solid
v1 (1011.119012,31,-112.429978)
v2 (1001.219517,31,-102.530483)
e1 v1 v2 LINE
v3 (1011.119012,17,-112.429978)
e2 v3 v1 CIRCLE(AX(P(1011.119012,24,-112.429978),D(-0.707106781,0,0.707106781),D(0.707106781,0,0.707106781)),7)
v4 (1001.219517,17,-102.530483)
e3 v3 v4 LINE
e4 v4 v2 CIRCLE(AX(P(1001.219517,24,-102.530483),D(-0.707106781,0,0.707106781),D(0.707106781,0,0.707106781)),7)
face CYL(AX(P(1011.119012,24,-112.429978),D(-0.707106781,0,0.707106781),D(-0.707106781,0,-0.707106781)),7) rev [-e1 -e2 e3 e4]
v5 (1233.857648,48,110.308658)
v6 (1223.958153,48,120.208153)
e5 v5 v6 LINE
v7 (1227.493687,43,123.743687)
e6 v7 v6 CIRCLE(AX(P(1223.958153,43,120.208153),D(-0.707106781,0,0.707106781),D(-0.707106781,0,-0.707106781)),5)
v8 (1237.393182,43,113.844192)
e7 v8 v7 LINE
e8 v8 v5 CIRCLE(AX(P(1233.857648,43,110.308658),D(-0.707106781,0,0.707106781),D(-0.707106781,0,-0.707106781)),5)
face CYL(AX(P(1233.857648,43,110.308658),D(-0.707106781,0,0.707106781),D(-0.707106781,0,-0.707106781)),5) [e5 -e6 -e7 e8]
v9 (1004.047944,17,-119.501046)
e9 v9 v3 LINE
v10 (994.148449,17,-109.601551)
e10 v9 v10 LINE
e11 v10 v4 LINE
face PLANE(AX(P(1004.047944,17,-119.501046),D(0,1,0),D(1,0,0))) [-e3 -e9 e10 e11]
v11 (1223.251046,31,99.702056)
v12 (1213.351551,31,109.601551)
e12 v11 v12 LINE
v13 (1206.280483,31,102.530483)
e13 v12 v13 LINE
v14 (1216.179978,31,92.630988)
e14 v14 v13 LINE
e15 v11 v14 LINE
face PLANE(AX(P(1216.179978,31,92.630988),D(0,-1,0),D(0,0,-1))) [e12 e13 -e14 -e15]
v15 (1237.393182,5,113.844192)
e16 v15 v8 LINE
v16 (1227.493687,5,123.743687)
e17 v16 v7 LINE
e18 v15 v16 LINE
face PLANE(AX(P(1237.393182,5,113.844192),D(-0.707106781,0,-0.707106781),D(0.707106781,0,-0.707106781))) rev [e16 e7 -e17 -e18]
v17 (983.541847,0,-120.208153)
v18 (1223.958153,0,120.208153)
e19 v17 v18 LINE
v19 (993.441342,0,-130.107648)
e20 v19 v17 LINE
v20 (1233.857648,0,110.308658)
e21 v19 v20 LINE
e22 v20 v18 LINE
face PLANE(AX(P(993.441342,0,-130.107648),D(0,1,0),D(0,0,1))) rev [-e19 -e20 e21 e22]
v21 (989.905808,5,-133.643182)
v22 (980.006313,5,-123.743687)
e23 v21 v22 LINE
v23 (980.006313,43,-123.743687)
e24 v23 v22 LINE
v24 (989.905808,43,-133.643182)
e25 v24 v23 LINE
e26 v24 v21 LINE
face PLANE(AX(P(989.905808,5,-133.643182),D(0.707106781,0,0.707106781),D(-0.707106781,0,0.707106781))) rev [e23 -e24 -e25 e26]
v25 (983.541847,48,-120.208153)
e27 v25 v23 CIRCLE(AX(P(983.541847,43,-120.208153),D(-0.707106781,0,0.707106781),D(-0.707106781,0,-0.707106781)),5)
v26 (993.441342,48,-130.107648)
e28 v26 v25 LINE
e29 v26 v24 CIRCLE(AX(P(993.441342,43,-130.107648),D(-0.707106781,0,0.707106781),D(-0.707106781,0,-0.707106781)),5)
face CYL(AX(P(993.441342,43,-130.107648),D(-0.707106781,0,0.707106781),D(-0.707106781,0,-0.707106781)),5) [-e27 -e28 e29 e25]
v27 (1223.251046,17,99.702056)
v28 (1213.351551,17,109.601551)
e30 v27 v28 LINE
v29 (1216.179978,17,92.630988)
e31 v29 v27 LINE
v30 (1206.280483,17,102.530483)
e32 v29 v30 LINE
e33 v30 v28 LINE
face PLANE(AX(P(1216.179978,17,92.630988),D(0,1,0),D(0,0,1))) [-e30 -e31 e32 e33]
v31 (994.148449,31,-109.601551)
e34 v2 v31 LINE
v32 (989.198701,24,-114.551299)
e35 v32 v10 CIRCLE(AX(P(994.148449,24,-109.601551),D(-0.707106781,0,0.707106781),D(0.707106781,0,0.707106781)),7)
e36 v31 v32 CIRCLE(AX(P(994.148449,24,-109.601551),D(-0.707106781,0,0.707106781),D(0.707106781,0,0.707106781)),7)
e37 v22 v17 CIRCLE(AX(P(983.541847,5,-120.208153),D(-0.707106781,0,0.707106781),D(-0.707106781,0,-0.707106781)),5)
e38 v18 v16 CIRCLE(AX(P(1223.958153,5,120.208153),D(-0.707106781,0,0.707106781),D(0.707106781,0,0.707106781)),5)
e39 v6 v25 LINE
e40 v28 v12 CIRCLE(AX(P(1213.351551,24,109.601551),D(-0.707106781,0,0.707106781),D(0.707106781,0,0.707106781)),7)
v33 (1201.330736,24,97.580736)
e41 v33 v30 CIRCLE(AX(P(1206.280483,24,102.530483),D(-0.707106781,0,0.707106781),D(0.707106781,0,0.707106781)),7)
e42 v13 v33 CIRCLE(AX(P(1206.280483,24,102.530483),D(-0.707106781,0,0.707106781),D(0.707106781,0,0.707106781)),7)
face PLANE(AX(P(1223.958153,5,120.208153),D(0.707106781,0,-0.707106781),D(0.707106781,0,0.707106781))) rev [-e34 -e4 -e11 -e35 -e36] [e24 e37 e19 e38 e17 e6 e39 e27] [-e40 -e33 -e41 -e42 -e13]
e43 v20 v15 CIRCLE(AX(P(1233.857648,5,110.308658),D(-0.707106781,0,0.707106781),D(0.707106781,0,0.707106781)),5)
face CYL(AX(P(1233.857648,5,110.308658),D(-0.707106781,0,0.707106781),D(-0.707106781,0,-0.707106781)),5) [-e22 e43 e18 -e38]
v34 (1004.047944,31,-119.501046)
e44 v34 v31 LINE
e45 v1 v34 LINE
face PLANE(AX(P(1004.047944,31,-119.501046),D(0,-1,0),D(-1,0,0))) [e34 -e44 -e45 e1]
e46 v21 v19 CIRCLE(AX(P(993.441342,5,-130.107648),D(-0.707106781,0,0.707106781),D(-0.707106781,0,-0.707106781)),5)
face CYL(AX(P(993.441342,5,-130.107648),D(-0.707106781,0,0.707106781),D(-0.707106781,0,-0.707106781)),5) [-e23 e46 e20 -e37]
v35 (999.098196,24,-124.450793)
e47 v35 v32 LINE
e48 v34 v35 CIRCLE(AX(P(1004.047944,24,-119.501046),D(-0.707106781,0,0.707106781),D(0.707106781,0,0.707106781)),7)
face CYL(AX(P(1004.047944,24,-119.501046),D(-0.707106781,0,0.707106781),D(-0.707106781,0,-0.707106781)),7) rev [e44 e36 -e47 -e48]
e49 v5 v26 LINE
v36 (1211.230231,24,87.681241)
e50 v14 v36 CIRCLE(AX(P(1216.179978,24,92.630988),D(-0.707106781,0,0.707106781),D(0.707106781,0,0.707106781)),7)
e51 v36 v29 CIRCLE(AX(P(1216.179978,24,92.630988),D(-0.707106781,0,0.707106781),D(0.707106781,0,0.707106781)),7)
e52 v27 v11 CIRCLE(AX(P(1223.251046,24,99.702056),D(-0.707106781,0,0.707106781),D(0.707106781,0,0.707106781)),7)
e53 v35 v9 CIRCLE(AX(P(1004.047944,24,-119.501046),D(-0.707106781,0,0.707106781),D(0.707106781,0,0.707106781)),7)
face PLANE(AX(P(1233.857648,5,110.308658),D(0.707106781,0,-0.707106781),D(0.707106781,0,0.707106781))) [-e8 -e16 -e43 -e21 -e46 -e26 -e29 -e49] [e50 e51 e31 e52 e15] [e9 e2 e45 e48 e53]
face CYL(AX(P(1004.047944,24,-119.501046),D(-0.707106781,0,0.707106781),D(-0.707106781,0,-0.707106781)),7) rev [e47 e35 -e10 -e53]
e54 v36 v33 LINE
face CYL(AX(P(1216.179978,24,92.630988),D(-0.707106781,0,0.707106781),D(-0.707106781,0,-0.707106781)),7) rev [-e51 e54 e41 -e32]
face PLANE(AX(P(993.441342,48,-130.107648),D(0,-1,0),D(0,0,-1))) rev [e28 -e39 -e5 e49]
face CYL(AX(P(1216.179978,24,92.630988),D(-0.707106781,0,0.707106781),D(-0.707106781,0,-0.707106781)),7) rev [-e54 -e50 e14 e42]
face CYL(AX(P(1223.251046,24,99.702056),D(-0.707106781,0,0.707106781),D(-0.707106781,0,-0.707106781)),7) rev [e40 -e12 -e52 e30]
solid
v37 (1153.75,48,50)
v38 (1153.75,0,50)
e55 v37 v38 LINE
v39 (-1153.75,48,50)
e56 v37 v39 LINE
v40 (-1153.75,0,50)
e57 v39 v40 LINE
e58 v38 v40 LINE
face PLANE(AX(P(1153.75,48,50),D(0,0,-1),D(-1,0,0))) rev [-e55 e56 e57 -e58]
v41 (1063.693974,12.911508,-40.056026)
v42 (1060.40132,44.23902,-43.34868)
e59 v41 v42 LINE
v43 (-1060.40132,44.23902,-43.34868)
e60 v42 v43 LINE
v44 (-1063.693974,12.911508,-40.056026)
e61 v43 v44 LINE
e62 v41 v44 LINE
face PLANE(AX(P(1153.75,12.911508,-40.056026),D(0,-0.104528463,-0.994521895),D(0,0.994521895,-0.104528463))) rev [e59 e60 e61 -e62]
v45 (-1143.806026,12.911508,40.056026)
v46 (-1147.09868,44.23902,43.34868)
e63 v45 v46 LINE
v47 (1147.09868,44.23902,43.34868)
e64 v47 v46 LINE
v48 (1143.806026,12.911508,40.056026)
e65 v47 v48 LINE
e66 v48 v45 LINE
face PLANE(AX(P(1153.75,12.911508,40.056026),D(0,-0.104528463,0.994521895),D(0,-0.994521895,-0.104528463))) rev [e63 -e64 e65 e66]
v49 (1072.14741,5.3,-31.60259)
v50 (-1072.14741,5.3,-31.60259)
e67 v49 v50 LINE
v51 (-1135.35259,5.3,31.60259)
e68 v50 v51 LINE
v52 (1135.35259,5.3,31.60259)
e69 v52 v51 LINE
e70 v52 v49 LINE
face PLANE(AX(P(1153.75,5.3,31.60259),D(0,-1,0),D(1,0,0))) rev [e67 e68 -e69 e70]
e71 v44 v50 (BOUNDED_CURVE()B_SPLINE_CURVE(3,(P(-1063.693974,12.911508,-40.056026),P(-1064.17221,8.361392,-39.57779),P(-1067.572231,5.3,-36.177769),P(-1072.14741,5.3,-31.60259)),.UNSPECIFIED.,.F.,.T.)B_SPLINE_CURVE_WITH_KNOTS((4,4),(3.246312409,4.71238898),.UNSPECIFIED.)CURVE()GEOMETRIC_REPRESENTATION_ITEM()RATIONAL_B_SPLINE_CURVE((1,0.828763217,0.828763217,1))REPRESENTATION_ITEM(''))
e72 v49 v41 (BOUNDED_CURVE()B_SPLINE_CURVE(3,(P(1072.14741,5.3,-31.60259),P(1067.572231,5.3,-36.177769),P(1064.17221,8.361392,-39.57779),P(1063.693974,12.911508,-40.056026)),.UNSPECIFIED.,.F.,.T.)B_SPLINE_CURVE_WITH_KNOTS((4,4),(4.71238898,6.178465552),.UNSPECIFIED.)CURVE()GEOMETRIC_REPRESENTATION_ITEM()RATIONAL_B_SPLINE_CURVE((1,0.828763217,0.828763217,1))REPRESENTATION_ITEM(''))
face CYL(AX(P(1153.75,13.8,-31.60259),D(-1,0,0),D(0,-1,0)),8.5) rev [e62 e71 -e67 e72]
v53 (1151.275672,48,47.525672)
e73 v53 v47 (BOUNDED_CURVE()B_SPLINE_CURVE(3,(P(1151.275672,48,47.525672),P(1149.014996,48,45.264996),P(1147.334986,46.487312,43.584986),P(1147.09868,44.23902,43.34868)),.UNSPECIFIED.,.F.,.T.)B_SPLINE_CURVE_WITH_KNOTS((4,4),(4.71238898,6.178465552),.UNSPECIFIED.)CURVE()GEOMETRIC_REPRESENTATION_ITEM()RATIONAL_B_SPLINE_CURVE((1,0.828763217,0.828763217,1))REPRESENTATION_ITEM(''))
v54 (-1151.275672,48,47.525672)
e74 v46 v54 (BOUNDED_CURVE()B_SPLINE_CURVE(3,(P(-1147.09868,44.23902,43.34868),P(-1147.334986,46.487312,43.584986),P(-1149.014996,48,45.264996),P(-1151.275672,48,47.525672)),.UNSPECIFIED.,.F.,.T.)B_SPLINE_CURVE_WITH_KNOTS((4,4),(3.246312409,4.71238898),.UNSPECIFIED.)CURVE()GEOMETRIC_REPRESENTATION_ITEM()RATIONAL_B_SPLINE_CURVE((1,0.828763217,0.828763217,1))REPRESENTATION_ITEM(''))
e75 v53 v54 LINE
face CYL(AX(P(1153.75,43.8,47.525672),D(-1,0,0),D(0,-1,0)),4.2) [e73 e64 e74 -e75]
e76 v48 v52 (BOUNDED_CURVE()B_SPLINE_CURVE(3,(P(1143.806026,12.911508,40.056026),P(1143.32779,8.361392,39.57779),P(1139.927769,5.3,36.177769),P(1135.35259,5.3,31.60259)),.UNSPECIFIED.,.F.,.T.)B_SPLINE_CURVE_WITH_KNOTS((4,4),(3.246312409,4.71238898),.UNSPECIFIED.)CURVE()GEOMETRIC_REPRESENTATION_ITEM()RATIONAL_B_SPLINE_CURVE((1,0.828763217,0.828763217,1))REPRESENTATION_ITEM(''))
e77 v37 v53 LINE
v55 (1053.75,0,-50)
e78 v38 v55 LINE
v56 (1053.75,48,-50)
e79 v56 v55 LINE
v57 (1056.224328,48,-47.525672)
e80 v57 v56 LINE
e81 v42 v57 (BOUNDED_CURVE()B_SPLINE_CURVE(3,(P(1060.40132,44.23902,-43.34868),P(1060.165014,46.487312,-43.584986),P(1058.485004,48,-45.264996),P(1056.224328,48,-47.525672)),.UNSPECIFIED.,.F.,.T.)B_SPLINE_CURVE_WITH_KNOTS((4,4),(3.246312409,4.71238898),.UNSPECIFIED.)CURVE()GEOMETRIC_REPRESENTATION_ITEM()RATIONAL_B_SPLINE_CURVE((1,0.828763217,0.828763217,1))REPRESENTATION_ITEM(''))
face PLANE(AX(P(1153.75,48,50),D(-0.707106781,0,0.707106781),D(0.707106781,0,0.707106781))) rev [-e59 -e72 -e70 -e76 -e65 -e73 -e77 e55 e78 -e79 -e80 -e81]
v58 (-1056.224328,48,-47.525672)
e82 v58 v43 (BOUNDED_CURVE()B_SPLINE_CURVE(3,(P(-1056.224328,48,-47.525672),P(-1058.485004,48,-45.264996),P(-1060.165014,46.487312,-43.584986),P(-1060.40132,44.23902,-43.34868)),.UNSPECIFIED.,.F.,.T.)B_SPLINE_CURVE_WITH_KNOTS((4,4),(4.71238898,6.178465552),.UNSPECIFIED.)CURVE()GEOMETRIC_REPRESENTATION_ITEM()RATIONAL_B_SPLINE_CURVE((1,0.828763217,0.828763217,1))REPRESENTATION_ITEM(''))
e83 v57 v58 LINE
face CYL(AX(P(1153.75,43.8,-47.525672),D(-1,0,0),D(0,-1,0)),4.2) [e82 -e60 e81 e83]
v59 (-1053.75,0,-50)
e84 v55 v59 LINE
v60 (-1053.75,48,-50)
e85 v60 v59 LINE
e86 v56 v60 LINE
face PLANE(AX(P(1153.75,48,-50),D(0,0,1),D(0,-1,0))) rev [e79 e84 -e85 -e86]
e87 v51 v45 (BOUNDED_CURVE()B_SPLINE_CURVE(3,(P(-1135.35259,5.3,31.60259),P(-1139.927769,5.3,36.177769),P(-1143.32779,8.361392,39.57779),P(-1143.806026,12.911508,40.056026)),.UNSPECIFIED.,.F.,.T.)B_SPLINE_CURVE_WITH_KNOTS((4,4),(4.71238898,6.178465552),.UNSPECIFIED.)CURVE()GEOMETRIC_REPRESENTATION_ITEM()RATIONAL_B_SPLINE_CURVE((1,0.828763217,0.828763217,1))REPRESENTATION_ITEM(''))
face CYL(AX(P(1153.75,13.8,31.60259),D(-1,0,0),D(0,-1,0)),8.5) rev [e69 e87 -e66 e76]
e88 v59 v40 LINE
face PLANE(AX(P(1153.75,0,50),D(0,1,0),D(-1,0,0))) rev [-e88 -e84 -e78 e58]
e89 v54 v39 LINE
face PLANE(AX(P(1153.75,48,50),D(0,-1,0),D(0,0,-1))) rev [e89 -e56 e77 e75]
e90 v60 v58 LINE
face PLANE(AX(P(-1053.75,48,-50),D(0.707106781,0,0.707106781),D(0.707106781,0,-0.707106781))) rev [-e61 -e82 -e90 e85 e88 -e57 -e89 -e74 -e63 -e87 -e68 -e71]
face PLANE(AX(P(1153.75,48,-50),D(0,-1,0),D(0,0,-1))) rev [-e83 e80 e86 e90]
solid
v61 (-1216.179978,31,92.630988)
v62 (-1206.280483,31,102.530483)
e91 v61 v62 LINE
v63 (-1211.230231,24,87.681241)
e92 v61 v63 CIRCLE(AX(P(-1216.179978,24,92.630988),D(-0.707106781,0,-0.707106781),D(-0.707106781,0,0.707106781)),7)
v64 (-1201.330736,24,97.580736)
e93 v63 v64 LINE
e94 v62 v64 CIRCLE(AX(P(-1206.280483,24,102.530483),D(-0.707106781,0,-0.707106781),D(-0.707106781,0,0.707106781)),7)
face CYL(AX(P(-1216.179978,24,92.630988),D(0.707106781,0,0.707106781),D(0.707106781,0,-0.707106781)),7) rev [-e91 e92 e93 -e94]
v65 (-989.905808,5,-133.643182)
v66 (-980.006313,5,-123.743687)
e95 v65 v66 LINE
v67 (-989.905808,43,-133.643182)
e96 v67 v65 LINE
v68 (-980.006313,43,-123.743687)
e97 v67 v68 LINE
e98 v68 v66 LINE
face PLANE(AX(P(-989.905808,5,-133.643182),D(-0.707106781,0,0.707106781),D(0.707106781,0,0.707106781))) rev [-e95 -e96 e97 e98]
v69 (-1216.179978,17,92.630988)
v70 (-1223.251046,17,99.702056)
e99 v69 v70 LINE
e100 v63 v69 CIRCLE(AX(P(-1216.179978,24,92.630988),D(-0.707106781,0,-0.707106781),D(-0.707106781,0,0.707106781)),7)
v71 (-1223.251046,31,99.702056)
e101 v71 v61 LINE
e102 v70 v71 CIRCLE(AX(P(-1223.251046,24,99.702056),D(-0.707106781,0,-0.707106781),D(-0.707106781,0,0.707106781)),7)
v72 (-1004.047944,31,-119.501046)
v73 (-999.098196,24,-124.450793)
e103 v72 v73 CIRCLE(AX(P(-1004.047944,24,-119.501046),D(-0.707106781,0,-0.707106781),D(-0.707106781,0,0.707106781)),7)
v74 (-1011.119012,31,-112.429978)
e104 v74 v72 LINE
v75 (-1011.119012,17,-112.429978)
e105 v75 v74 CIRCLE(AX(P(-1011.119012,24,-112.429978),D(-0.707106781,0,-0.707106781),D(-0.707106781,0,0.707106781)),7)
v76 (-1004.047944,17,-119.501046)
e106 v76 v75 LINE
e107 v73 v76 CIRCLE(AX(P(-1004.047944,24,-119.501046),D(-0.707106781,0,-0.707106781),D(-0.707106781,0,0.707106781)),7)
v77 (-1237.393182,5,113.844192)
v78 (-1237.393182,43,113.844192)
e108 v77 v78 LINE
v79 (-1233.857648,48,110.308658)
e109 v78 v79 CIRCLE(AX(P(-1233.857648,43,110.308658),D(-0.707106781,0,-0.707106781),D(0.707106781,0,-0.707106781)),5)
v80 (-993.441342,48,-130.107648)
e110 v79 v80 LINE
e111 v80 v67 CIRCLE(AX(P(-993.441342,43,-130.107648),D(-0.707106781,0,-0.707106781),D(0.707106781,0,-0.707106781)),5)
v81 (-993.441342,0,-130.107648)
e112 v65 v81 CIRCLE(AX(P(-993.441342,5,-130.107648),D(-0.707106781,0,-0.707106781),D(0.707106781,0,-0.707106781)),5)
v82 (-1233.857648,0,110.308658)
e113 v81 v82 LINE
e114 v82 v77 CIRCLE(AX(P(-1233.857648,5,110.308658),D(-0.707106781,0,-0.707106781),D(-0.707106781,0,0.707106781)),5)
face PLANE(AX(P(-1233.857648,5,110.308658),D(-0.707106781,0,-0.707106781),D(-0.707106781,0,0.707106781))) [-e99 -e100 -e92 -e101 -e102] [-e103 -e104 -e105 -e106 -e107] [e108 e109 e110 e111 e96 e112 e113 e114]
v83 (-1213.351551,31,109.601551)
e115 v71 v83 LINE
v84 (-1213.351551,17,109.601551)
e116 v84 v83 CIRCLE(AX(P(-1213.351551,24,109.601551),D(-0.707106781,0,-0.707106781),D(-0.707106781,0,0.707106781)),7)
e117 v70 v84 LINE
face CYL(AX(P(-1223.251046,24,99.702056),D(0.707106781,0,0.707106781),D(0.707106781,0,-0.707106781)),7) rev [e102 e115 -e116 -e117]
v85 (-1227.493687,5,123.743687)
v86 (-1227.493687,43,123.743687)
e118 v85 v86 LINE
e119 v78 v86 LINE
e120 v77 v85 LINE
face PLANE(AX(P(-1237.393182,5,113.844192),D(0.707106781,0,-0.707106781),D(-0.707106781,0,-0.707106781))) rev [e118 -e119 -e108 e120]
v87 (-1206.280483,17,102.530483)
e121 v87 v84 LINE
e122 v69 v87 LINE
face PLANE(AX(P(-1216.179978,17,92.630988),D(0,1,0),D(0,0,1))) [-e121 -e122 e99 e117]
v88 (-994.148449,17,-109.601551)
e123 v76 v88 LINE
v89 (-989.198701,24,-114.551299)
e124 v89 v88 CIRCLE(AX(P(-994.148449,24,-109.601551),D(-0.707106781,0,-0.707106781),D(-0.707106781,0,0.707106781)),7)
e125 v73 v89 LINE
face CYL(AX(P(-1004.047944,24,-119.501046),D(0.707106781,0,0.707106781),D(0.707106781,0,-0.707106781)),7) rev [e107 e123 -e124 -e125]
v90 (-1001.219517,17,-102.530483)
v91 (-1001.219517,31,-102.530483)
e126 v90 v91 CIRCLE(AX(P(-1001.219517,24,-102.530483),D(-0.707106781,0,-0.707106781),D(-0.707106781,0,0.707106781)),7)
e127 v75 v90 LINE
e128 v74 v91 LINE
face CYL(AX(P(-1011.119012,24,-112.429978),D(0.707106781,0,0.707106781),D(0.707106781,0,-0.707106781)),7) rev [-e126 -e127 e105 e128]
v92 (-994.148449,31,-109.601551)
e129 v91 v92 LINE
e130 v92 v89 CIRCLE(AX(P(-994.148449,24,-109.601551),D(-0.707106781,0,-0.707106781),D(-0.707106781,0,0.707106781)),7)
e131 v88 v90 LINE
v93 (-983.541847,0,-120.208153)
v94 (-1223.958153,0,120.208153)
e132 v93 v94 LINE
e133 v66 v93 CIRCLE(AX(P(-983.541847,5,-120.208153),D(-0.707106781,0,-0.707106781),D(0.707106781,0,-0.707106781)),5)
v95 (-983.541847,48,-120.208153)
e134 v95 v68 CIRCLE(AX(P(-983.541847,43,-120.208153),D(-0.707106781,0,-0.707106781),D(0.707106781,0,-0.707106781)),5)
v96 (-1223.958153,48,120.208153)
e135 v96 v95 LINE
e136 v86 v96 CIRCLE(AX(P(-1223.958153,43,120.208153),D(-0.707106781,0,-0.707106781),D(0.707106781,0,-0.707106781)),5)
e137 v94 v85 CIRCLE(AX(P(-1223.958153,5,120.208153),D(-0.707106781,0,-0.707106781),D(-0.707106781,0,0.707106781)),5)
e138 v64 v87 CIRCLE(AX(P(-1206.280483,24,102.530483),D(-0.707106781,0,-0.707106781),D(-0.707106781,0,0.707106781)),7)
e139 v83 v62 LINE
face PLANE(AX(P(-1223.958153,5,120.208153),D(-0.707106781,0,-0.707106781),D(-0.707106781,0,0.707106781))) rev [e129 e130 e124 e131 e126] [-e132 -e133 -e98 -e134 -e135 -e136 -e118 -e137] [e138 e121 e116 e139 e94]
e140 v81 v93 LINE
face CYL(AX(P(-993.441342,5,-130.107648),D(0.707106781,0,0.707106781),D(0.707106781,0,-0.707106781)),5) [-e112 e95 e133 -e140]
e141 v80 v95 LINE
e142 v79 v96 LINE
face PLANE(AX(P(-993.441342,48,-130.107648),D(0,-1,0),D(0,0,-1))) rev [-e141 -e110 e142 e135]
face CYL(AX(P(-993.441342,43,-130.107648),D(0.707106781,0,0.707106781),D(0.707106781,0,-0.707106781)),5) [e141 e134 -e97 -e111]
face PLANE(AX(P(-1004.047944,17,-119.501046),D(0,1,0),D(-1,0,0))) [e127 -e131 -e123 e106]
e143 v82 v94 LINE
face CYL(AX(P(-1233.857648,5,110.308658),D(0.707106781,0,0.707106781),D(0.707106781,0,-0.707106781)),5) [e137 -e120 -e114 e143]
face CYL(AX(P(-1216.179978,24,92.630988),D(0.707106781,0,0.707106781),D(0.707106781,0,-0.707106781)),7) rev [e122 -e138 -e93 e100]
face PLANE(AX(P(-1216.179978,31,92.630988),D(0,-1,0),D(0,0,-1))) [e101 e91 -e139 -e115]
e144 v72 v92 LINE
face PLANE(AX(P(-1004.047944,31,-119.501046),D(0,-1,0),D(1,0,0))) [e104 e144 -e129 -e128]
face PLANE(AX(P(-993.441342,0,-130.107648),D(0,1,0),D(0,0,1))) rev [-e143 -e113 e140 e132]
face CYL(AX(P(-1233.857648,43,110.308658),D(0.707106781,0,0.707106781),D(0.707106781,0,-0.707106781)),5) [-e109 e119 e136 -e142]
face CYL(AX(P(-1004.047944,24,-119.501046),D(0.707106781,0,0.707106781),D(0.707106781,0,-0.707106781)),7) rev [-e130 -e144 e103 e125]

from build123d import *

# Parameters (mm, degrees)
GB_T707_1988_HOT_ROLLED_CHANNEL_10_1_DEPTH = 2307.5
CUT_EXTRUDE1_DEPTH                         = 1156.830031839
BOSS_EXTRUDE1_DEPTH                        = 14


with BuildPart() as part:
    # Sketch1 → Gb／t707-1988 Hot-Rolled Channel 10(1) (new body)
    with BuildSketch(Plane(origin=(-1153.75, 0, -50), x_dir=(0, 1, 0), z_dir=(1, 0, 0))):
        with BuildLine():
            Line((48, 100), (0, 100))
            Line((0, 100), (0, 0))
            Line((0, 0), (48, 0))
            Line((48, 0), (48, 2.474327591))
            ThreePointArc((48, 2.474327591), (46.921208267, 5.284676138), (44.239019546, 6.651319552))
            Line((44.239019546, 6.651319552), (12.911508062, 9.943973689))
            ThreePointArc((12.911508062, 9.943973689), (7.483268983, 12.709799645), (5.3, 18.397409799))
            Line((5.3, 18.397409799), (5.3, 81.602590201))
            ThreePointArc((5.3, 81.602590201), (7.483268983, 87.290200355), (12.911508062, 90.056026311))
            Line((12.911508062, 90.056026311), (44.239019546, 93.348680448))
            ThreePointArc((44.239019546, 93.348680448), (46.921208267, 94.715323862), (48, 97.525672409))
            Line((48, 97.525672409), (48, 100))
        make_face()
    extrude(amount=GB_T707_1988_HOT_ROLLED_CHANNEL_10_1_DEPTH)

    # Sketch3 → Cut-Extrude1 (cut, through all)
    with BuildSketch(Plane.XZ):
        Polygon((1153.75, 50), (1053.75, -50), (1153.75, -50), align=None)
        Polygon((-1153.75, 50), (-1153.75, -50), (-1053.75, -50), align=None)
    extrude(amount=-CUT_EXTRUDE1_DEPTH, mode=Mode.SUBTRACT)


with BuildPart() as body_2:
    # Sketch4 → Boss-Extrude1 (new body)
    with BuildSketch(Plane(origin=(-551.875, 0, -551.875), x_dir=(-0.7071067811865479, 0, 0.7071067811865472), z_dir=(-0.7071067811865472, 0, -0.7071067811865479))):
        with BuildLine():
            Line((610.469109735, 0), (950.469109735, 0))
            ThreePointArc((950.469109735, 0), (954.004643641, 1.464466094), (955.469109735, 5))
            Line((955.469109735, 5), (955.469109735, 43))
            ThreePointArc((955.469109735, 43), (954.004643641, 46.535533906), (950.469109735, 48))
            Line((950.469109735, 48), (610.469109735, 48))
            ThreePointArc((610.469109735, 48), (606.933575829, 46.535533906), (605.469109735, 43))
            Line((605.469109735, 43), (605.469109735, 5))
            ThreePointArc((605.469109735, 5), (606.933575829, 1.464466094), (610.469109735, 0))
        make_face()
        with BuildLine():
            Line((925.469109735, 31), (935.469109735, 31))
            ThreePointArc((935.469109735, 31), (942.469109735, 24), (935.469109735, 17))
            Line((935.469109735, 17), (925.469109735, 17))
            ThreePointArc((925.469109735, 17), (918.469109735, 24), (925.469109735, 31))
        make_face(mode=Mode.SUBTRACT)
        with BuildLine():
            Line((625.469109735, 31), (635.469109735, 31))
            ThreePointArc((635.469109735, 31), (642.469109735, 24), (635.469109735, 17))
            Line((635.469109735, 17), (625.469109735, 17))
            ThreePointArc((625.469109735, 17), (618.469109735, 24), (625.469109735, 31))
        make_face(mode=Mode.SUBTRACT)
    extrude(amount=BOSS_EXTRUDE1_DEPTH)


with BuildPart() as body_3:
    # Mirror1: mirrored copy
    add(body_2.part.mirror(Plane(origin=(0, 0, 0), x_dir=(0, 0, 1), z_dir=(1, 0, 0))))


solid = Compound([part.part, body_2.part, body_3.part])
